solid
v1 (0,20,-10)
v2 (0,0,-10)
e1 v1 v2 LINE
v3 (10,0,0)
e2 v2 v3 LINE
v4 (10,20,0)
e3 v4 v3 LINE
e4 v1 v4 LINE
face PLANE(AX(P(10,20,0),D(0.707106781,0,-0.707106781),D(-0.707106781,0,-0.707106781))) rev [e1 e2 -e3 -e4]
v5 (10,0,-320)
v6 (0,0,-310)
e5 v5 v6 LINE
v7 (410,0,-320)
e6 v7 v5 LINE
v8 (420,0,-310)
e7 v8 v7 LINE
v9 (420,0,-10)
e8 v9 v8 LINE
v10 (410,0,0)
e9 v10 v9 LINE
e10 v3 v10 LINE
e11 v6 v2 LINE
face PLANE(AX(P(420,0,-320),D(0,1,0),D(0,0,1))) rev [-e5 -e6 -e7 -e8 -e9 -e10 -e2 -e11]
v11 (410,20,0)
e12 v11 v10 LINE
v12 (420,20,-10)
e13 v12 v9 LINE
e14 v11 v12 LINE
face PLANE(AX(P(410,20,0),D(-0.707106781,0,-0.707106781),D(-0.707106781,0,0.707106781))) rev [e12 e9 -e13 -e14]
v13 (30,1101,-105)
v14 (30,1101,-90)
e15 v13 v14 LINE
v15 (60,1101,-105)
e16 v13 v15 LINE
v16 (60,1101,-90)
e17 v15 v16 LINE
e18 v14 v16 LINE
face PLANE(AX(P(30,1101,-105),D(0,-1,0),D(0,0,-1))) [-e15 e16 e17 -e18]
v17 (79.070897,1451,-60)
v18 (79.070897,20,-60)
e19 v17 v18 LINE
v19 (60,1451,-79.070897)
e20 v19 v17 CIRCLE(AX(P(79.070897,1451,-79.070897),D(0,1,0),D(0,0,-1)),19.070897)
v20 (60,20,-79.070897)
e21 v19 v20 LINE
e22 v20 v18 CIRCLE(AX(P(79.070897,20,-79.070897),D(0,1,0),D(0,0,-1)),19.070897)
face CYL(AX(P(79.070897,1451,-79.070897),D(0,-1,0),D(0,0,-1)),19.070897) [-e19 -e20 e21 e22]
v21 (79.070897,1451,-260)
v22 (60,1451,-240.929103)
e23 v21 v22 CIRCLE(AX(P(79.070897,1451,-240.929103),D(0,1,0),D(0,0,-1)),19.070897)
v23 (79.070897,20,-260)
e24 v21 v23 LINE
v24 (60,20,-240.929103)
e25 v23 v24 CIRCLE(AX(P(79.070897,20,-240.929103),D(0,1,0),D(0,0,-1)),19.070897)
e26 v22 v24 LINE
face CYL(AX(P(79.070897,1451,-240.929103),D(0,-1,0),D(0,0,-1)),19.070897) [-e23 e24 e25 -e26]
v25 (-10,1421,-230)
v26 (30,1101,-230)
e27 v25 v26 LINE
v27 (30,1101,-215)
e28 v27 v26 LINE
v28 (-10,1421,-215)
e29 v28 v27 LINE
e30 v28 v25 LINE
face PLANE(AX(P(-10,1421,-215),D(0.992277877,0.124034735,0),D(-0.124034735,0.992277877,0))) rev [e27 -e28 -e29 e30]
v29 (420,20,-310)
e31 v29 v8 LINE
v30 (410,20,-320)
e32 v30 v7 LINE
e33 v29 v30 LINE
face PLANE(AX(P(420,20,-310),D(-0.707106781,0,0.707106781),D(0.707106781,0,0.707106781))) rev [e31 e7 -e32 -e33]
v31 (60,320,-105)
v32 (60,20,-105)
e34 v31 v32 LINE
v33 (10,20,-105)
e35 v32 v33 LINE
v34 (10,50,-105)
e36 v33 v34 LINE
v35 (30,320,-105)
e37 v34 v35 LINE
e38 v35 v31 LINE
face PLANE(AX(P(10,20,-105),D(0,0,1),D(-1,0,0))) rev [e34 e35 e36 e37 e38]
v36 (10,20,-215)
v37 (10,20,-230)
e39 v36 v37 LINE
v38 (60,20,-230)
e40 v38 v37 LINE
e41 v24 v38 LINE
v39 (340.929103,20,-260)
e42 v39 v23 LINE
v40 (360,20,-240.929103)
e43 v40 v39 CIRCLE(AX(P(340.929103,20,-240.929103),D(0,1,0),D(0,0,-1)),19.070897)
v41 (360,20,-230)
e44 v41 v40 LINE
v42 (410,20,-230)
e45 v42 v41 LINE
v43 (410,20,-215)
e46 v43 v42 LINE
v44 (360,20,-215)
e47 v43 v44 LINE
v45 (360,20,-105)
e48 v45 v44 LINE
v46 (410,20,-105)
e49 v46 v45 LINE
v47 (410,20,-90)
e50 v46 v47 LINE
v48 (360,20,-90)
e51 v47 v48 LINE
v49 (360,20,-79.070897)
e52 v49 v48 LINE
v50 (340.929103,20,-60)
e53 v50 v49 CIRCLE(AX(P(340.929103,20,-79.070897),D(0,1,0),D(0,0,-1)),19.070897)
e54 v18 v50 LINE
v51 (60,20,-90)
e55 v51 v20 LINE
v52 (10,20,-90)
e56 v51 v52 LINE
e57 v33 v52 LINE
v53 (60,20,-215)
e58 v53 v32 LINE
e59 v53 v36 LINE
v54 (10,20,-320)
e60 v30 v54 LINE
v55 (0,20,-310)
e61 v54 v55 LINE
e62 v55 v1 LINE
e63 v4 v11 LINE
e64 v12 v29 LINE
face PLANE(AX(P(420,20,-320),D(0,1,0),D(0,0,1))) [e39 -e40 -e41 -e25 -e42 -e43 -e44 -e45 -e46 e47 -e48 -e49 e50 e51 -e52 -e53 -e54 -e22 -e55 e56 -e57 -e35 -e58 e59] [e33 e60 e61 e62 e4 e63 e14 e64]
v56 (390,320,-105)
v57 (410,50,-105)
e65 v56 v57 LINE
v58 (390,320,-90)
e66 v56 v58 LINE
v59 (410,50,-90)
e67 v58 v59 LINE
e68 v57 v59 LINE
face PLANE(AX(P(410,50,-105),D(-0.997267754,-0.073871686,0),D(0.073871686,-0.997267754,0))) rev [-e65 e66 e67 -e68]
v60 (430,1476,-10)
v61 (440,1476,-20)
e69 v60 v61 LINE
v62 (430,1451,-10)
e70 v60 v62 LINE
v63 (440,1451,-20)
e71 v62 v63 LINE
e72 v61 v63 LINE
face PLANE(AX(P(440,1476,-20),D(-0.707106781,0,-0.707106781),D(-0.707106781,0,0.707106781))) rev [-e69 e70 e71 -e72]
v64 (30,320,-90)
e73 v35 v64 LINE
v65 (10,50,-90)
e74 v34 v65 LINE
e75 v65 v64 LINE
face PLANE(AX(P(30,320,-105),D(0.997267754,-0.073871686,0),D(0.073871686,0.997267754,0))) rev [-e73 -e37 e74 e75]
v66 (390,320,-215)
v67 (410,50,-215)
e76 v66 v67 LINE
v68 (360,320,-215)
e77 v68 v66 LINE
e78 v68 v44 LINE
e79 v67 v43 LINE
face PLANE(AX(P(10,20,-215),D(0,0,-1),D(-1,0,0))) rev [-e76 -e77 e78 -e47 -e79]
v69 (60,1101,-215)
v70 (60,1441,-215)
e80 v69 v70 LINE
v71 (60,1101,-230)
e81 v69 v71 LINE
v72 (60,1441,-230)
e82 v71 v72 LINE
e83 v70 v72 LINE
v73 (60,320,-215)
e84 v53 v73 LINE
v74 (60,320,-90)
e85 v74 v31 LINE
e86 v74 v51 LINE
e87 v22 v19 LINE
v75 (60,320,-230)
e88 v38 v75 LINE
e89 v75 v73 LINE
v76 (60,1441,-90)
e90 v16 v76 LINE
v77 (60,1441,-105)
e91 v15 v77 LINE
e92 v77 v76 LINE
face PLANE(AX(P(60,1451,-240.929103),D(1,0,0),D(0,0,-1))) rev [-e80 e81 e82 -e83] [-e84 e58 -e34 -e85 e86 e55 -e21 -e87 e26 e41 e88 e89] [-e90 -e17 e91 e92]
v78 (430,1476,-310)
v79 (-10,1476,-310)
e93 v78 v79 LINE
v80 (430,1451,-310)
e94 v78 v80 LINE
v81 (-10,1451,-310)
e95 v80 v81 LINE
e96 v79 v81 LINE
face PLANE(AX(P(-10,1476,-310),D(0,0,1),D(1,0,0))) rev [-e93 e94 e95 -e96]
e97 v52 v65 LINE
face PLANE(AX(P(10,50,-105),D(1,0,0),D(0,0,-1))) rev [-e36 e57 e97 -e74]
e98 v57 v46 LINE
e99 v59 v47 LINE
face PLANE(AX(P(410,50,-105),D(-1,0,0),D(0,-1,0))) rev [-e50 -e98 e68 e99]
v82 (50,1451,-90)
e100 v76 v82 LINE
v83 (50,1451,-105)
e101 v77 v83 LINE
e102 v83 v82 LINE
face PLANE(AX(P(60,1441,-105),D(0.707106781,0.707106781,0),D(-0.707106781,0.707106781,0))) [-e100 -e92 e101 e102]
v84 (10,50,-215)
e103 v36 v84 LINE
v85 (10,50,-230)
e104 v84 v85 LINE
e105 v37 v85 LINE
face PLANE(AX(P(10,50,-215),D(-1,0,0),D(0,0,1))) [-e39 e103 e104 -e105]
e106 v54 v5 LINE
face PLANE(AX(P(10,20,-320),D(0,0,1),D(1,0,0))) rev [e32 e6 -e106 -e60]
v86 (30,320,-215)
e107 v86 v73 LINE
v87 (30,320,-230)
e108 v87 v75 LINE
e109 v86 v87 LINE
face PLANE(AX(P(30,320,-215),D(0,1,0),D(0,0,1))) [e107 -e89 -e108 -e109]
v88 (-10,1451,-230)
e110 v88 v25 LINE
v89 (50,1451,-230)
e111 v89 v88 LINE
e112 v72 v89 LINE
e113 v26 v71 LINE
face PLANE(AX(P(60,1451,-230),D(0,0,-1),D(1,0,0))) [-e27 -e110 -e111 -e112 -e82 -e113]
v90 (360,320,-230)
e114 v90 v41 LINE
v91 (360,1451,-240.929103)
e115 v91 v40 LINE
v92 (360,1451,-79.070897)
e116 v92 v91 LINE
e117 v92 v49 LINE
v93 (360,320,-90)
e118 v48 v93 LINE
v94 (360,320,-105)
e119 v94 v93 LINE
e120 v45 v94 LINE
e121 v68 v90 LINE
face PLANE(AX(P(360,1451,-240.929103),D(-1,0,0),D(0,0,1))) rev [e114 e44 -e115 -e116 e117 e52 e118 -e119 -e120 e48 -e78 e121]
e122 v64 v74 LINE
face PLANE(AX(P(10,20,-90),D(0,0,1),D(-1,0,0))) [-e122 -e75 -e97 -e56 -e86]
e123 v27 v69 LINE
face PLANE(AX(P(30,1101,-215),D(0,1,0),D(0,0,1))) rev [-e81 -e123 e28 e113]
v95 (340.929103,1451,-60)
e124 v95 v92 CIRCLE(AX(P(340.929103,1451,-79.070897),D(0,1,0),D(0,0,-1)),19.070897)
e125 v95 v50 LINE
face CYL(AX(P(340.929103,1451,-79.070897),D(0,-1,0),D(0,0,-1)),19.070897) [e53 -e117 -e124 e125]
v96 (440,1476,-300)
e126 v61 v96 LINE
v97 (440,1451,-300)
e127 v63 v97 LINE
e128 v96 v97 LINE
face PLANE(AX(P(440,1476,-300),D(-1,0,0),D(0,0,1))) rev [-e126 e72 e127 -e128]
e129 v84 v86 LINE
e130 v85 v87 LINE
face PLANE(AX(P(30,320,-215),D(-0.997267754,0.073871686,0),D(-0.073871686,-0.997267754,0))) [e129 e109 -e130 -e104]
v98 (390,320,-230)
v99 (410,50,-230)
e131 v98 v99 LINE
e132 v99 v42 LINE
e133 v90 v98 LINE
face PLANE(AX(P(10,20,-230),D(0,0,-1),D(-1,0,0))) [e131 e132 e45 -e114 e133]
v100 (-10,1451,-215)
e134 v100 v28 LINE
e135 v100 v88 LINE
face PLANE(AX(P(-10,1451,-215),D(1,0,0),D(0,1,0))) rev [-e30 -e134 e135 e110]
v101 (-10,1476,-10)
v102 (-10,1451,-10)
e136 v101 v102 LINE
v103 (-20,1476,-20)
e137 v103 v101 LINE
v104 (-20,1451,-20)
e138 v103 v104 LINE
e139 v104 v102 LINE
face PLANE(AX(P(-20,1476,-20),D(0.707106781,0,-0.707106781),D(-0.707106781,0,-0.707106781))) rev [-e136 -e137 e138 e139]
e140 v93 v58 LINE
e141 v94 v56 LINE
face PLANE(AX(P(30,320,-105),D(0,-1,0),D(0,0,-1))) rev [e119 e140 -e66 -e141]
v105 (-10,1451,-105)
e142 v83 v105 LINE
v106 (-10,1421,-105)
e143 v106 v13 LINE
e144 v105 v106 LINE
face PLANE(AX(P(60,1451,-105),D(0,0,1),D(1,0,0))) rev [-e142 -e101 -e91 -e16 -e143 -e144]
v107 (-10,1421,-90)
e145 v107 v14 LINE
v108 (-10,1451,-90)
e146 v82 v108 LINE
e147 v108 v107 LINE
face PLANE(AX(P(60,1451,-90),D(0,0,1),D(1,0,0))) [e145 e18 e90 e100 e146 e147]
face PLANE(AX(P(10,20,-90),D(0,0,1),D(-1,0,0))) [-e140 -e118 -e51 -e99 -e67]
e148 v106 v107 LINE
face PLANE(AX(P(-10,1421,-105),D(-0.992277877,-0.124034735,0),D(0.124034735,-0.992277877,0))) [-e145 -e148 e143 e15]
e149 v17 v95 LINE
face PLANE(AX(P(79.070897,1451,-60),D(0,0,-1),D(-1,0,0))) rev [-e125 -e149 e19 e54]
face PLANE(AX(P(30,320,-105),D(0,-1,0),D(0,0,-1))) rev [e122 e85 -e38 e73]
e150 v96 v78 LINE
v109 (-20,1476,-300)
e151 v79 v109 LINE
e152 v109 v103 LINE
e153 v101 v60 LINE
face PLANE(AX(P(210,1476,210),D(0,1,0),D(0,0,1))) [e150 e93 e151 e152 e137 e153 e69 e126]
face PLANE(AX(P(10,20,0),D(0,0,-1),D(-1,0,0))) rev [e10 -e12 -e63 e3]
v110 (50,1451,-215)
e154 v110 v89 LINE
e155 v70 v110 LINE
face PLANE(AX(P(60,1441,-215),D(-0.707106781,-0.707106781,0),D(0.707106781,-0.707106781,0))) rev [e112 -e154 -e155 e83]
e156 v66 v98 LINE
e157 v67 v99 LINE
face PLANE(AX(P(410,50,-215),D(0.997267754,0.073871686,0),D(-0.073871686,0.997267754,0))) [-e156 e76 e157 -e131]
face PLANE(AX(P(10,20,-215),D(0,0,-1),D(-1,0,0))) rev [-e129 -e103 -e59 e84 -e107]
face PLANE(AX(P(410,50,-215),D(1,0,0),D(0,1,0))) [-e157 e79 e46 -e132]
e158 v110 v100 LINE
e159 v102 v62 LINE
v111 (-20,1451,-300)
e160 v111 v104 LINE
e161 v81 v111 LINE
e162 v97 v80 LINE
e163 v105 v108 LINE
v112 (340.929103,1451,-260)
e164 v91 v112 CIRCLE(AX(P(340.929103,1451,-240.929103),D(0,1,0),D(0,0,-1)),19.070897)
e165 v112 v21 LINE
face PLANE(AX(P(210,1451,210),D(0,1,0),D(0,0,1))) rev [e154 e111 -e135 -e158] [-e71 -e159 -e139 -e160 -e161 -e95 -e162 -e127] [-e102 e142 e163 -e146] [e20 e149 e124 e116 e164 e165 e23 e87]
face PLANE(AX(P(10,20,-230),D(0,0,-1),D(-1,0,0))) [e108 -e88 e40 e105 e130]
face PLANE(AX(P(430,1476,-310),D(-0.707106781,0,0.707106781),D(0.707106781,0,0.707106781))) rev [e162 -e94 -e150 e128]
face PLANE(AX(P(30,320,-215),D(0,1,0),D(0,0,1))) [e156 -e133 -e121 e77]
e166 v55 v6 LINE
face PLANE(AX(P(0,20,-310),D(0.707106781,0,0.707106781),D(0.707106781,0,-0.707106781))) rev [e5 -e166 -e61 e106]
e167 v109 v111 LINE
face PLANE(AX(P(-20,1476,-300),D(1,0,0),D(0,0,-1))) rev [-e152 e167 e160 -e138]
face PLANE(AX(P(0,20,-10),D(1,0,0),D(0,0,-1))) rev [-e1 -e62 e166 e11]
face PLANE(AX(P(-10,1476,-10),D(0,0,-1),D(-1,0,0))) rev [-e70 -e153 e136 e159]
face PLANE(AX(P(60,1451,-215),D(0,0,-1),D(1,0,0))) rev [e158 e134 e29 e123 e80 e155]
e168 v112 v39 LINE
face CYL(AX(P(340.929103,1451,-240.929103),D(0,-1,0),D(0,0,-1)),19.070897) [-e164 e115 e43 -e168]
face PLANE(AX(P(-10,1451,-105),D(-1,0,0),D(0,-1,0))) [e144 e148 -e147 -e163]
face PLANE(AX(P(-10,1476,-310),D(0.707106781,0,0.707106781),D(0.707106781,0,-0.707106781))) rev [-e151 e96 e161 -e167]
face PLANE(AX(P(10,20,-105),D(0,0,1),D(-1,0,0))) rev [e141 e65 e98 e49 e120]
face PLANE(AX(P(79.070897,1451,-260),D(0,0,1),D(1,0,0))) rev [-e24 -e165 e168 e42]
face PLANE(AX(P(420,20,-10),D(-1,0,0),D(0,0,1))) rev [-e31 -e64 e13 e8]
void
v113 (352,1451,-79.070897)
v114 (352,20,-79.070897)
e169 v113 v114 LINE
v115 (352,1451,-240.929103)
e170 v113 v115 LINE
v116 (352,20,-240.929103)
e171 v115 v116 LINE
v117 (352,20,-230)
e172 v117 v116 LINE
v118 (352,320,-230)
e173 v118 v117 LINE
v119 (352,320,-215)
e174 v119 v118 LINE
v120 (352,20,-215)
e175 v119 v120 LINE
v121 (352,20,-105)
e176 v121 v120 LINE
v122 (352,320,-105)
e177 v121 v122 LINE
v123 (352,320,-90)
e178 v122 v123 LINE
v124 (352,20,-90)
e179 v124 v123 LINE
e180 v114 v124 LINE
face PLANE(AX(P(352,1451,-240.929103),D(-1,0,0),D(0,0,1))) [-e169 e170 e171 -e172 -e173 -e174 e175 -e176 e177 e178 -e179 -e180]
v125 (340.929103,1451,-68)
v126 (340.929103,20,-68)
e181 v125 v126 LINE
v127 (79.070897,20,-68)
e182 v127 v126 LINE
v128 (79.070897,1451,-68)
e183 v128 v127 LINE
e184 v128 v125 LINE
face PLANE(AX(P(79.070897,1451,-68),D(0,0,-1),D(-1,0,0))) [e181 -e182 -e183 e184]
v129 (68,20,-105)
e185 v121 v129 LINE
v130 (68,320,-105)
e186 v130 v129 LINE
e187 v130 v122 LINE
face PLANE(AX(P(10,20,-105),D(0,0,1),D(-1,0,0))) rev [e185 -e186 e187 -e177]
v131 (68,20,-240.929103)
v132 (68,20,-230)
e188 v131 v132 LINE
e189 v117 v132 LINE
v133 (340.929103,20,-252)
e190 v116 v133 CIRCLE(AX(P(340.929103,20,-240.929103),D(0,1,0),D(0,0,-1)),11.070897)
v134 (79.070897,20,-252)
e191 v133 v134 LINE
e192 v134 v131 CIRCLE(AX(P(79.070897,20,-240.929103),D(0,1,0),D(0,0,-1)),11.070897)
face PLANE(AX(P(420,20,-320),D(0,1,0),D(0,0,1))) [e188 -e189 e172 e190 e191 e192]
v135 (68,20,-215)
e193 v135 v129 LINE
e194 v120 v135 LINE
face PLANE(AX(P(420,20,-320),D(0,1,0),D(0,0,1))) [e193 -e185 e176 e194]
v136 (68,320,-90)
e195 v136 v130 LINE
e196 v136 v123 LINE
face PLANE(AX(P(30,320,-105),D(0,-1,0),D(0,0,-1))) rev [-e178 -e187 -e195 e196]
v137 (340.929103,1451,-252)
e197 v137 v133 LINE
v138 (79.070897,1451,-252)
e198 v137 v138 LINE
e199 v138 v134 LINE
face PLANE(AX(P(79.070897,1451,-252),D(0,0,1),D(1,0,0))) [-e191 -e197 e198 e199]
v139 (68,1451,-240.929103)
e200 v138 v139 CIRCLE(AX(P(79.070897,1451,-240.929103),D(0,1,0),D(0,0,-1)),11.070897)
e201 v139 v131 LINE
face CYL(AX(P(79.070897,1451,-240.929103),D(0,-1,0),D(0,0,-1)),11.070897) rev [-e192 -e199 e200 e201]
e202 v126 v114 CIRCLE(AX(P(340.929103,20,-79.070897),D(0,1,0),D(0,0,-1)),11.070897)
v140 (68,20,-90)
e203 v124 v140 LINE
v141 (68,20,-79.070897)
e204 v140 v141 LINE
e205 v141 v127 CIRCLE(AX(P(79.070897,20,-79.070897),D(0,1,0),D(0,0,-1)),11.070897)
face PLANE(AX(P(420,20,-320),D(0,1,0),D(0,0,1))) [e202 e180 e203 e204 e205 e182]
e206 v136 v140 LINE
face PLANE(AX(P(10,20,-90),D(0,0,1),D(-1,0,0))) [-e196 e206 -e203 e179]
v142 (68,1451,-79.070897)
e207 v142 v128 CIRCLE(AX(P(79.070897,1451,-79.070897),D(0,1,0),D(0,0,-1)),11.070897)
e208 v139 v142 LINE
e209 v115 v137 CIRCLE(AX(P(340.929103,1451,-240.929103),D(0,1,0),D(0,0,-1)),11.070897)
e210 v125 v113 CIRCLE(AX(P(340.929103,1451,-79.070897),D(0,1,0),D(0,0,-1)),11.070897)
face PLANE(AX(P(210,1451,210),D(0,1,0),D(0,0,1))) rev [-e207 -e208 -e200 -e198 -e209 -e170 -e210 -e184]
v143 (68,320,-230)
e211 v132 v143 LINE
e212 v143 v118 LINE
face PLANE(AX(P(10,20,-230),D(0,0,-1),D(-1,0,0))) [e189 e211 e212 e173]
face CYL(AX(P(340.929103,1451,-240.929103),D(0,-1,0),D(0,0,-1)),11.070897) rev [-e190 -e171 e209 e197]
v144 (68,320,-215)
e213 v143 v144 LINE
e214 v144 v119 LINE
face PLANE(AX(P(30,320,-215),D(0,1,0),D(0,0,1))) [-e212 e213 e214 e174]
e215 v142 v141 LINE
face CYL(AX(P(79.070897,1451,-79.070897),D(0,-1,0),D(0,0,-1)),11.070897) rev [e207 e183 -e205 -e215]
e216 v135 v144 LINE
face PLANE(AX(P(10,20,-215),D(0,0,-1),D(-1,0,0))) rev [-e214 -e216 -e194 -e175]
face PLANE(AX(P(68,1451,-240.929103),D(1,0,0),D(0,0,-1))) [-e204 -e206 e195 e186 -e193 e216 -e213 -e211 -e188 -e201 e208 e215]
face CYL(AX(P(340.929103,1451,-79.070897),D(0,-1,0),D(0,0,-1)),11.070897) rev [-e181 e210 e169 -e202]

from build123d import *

# Parameters (mm, degrees)
BOSS_EXTRUDE1_DEPTH = 20
BOSS_EXTRUDE2_DEPTH = 1431
BOSS_EXTRUDE3_DEPTH = 25
BOSS_EXTRUDE4_START = -30
BOSS_EXTRUDE4_DEPTH = 15
BOSS_EXTRUDE7_START = -30
BOSS_EXTRUDE7_DEPTH = 15


with BuildPart() as part:
    # Sketch1 → Boss-Extrude1 (new body)
    with BuildSketch(Plane(origin=(0, 0, 0), x_dir=(1, 0, 0), z_dir=(0, 1, 0))):
        Polygon((0, 310), (10, 320), (410, 320), (420, 310), (420, 10), (410, 0), (10, 0), (0, 10), align=None)
    extrude(amount=BOSS_EXTRUDE1_DEPTH)

    # Sketch2 → Boss-Extrude2 (add)
    with BuildSketch(Plane(origin=(0, 20, 0), x_dir=(1, 0, 0), z_dir=(0, 1, 0))):
        with BuildLine():
            Line((79.070897456, 260), (340.929102544, 260))
            ThreePointArc((340.929102544, 260), (354.414263459, 254.414263459), (360, 240.929102544))
            Line((360, 240.929102544), (360, 79.070897456))
            ThreePointArc((360, 79.070897456), (354.414263459, 65.585736541), (340.929102544, 60))
            Line((340.929102544, 60), (79.070897456, 60))
            ThreePointArc((79.070897456, 60), (65.585736541, 65.585736541), (60, 79.070897456))
            Line((60, 79.070897456), (60, 240.929102544))
            ThreePointArc((60, 240.929102544), (65.585736541, 254.414263459), (79.070897456, 260))
        make_face()
        with BuildLine():
            Line((79.070897456, 252), (340.929102544, 252))
            ThreePointArc((340.929102544, 252), (348.757409209, 248.757409209), (352, 240.929102544))
            Line((352, 240.929102544), (352, 79.070897456))
            ThreePointArc((352, 79.070897456), (348.757409209, 71.242590791), (340.929102544, 68))
            Line((340.929102544, 68), (79.070897456, 68))
            ThreePointArc((79.070897456, 68), (71.242590791, 71.242590791), (68, 79.070897456))
            Line((68, 79.070897456), (68, 240.929102544))
            ThreePointArc((68, 240.929102544), (71.242590791, 248.757409209), (79.070897456, 252))
        make_face(mode=Mode.SUBTRACT)
    extrude(amount=BOSS_EXTRUDE2_DEPTH)

    # Sketch3 → Boss-Extrude3 (add)
    with BuildSketch(Plane(origin=(0, 1451, 0), x_dir=(1, 0, 0), z_dir=(0, 1, 0))):
        Polygon((-10, 310), (430, 310), (440, 300), (440, 20), (430, 10), (-10, 10), (-20, 20), (-20, 300), align=None)
    extrude(amount=BOSS_EXTRUDE3_DEPTH)

    # Sketch4 → Boss-Extrude4 (add)
    with BuildSketch(Plane(origin=(0, 0, -260), x_dir=(-1, 0, 0), z_dir=(0, 0, -1)).offset(BOSS_EXTRUDE4_START)):
        Polygon((-30, 320), (-10, 50), (-10, 20), (-410, 20), (-410, 50), (-390, 320), align=None)
    boss_extrude4 = extrude(amount=-BOSS_EXTRUDE4_DEPTH)

    # Mirror1: Boss-Extrude4 across plane
    add(boss_extrude4.mirror(Plane.XY.offset(-160)))

    # Sketch5 → Boss-Extrude7 (add)
    with BuildSketch(Plane.XY.offset(-60).offset(BOSS_EXTRUDE7_START)):
        Polygon((60, 1441), (50, 1451), (-10, 1451), (-10, 1421), (30, 1101), (60, 1101), align=None)
    boss_extrude7 = extrude(amount=-BOSS_EXTRUDE7_DEPTH)

    # Mirror5: Boss-Extrude7 across plane
    add(boss_extrude7.mirror(Plane.XY.offset(-160)))


solid = part.part
